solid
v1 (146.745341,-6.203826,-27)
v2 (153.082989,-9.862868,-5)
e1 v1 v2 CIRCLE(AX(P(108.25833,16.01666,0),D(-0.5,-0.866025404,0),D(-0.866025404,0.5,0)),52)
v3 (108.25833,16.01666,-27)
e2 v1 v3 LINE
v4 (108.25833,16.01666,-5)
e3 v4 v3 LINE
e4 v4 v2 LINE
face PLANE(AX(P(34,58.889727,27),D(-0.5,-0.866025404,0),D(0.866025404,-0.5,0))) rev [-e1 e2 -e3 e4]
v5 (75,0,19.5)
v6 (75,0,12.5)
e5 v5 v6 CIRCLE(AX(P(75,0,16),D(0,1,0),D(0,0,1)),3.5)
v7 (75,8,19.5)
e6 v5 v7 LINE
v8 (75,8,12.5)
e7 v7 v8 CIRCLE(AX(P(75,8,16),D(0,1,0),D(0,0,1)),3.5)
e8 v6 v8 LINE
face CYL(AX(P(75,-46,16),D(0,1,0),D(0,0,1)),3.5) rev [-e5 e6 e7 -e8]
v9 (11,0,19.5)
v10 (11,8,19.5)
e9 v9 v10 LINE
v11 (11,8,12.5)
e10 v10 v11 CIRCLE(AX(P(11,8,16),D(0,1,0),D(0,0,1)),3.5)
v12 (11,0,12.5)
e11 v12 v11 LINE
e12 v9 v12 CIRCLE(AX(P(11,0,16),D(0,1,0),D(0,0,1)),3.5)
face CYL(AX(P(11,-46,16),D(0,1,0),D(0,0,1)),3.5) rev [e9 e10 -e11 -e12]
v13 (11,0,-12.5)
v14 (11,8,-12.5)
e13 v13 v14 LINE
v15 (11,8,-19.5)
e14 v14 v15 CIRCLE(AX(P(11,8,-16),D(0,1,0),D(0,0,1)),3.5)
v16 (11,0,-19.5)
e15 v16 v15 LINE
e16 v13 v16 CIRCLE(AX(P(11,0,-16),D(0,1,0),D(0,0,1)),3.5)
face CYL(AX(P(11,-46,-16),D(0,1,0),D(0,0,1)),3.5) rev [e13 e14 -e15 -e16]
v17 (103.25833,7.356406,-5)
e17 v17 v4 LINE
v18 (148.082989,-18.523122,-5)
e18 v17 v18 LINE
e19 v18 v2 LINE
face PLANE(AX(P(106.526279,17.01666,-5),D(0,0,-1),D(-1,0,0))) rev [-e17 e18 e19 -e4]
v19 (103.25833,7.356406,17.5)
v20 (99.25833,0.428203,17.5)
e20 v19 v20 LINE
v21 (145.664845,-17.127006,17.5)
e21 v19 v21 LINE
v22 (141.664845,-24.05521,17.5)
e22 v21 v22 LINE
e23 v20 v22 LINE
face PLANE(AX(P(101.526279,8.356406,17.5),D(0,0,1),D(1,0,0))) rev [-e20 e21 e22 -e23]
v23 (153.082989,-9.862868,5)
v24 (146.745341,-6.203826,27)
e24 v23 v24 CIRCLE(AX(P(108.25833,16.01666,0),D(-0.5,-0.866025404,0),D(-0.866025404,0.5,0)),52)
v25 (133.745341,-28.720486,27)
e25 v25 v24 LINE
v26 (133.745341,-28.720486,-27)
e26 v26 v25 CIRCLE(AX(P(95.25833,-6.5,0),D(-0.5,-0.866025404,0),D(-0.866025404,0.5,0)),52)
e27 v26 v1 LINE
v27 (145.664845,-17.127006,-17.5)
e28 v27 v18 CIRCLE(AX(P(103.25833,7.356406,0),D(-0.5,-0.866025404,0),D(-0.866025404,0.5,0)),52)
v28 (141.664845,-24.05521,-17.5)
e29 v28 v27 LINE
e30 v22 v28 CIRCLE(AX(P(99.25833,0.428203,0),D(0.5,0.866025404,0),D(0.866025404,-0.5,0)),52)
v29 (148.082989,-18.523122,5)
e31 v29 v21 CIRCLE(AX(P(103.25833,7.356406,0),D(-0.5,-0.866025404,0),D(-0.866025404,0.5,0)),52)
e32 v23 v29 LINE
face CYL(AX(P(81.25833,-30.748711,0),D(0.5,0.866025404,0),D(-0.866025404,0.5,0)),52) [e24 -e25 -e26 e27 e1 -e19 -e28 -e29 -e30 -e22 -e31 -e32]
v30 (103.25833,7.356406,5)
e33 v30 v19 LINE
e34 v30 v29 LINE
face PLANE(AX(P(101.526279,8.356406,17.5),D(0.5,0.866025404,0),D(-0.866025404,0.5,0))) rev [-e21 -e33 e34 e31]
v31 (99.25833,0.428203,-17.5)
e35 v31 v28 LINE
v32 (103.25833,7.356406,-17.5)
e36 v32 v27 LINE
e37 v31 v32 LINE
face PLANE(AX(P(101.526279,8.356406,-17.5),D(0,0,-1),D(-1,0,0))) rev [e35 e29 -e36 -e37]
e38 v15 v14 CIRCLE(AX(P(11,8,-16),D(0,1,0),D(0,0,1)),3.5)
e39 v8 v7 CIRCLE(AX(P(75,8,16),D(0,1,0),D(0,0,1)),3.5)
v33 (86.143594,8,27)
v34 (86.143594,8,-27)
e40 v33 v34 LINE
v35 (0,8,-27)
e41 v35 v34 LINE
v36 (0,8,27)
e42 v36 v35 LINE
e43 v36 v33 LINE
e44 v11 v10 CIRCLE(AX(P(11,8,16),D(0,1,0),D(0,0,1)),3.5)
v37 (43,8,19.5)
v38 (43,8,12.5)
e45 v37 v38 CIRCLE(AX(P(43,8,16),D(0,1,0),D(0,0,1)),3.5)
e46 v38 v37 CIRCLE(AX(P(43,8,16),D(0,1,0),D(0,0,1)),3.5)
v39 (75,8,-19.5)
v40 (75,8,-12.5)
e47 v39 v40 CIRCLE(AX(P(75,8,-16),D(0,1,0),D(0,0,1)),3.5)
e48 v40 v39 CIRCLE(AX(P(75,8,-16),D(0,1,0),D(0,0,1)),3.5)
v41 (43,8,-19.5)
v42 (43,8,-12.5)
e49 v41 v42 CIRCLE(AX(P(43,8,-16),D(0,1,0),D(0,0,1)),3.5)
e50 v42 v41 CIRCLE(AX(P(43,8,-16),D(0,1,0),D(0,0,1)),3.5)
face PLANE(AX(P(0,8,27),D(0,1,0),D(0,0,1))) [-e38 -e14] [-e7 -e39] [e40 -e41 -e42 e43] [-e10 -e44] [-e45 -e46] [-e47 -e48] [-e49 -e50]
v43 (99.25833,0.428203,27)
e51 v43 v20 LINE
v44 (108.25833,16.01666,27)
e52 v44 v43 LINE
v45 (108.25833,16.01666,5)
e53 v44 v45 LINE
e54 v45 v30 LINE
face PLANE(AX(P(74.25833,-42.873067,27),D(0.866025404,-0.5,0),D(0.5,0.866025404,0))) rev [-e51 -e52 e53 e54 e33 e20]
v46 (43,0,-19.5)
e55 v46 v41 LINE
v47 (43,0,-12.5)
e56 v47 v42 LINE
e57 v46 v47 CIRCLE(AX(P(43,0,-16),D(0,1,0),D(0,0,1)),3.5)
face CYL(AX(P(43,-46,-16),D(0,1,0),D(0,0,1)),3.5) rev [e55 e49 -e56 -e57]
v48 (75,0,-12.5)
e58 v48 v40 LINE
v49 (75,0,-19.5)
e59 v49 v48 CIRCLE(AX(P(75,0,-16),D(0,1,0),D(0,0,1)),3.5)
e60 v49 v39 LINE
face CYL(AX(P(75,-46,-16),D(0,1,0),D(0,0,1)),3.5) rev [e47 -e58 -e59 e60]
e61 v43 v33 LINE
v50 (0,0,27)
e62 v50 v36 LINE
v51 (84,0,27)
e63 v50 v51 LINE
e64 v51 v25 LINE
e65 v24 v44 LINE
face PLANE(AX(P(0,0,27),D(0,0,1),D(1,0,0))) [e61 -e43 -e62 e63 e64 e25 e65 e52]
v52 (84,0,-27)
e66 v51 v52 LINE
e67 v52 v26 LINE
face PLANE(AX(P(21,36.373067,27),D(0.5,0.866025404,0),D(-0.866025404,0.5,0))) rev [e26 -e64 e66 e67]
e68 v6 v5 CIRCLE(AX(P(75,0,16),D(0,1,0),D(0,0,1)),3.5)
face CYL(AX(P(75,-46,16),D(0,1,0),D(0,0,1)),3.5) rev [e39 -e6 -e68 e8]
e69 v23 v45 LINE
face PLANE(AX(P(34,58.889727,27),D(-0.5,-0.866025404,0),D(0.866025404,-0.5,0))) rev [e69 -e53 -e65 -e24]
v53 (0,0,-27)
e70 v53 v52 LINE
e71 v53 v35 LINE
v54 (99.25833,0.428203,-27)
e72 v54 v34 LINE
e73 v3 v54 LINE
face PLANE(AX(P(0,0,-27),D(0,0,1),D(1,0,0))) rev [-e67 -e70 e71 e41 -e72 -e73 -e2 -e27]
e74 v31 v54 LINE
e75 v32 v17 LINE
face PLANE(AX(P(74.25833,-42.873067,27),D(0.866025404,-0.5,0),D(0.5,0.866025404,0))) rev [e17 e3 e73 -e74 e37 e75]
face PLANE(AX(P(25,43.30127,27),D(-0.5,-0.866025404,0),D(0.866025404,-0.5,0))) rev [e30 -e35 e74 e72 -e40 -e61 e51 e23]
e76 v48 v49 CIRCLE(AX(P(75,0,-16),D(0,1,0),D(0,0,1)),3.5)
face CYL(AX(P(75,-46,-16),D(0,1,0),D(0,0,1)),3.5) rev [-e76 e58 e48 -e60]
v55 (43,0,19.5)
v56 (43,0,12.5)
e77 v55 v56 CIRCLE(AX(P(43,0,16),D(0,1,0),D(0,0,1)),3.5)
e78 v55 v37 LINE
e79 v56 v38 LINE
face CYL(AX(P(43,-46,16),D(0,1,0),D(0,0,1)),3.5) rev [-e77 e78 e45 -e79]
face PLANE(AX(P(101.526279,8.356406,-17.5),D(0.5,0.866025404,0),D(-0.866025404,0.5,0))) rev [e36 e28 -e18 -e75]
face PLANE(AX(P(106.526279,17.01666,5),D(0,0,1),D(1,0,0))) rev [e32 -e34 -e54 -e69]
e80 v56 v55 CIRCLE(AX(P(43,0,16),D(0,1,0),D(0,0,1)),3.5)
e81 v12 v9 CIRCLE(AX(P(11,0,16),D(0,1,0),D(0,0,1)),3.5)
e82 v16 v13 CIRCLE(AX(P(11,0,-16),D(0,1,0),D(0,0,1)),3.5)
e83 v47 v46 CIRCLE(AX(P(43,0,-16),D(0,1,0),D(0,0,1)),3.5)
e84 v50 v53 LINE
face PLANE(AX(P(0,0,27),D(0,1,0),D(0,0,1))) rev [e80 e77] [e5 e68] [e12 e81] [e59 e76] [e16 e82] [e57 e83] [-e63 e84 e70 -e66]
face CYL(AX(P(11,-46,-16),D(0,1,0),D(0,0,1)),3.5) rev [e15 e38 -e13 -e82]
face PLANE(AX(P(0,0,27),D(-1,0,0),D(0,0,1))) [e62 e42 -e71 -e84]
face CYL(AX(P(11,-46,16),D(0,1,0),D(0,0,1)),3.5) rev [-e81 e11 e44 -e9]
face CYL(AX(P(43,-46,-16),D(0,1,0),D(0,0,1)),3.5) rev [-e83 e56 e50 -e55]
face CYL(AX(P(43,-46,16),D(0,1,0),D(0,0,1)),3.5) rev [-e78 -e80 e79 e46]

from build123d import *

# Parameters (mm, degrees)
BRACKET_BODY_DEPTH        = 27
CLAMP_SLOT_DEPTH          = 54
CLAMP_END_TRIM_DEPTH      = 54
MOUNTING_HOLES_SKETCH_R   = 3.5
MOUNTING_HOLES_6X_7_DEPTH = 54


with BuildPart() as part:
    # Bracket Profile Sketch → Bracket Body (new, symmetric)
    with BuildSketch(Plane.XY):
        Polygon((108.258330249, 16.016660498), (99.258330249, 0.42820323), (86.143593539, 8), (0, 8), (0, 0), (84, 0), (140.291651246, -32.5), (153.291651246, -9.983339502), align=None)
    extrude(amount=BRACKET_BODY_DEPTH, both=True)

    # Clamp Slot Sketch → Clamp Slot (cut)
    with BuildSketch(Plane(origin=(119.291651246, -68.873066959, 0), x_dir=(0, 0, -1), z_dir=(0.8660254037844386, -0.5000000000000001, 0))):
        Polygon((-17.5, 50), (17.5, 50), (17.5, 58), (5, 58), (5, 68), (-5, 68), (-5, 58), (-17.5, 58), align=None)
    extrude(amount=-CLAMP_SLOT_DEPTH, mode=Mode.SUBTRACT)

    # Clamp End Trim Sketch → Clamp End Trim (cut)
    with BuildSketch(Plane(origin=(34, 58.889727457, 0), x_dir=(0.8660254037844384, -0.5000000000000007, 0), z_dir=(0.5000000000000006, 0.8660254037844383, 0))):
        with BuildLine():
            Line((130.187106004, 27), (186.710578253, 27))
            Line((186.710578253, 27), (186.710578253, -27))
            Line((186.710578253, -27), (130.187106004, -27))
            ThreePointArc((130.187106004, -27), (137.746133918, 0), (130.187106004, 27))
        make_face()
    extrude(amount=-CLAMP_END_TRIM_DEPTH, mode=Mode.SUBTRACT)

    # Mounting Holes Sketch → Mounting Holes 6xØ7 (cut)
    with BuildSketch(Plane(origin=(0, 8, 0), x_dir=(1, 0, 0), z_dir=(0, 1, 0))):
        with Locations(Location((11, 16, 0), (0, 0, 270))):
            Circle(MOUNTING_HOLES_SKETCH_R)
        with Locations(Location((43, 16, 0), (0, 0, 270))):
            Circle(MOUNTING_HOLES_SKETCH_R)
        with Locations(Location((75, 16, 0), (0, 0, 270))):
            Circle(MOUNTING_HOLES_SKETCH_R)
        with Locations(Location((11, -16, 0), (0, 0, 270))):
            Circle(MOUNTING_HOLES_SKETCH_R)
        with Locations(Location((43, -16, 0), (0, 0, 270))):
            Circle(MOUNTING_HOLES_SKETCH_R)
        with Locations(Location((75, -16, 0), (0, 0, 270))):
            Circle(MOUNTING_HOLES_SKETCH_R)
    extrude(amount=-MOUNTING_HOLES_6X_7_DEPTH, mode=Mode.SUBTRACT)


solid = part.part
